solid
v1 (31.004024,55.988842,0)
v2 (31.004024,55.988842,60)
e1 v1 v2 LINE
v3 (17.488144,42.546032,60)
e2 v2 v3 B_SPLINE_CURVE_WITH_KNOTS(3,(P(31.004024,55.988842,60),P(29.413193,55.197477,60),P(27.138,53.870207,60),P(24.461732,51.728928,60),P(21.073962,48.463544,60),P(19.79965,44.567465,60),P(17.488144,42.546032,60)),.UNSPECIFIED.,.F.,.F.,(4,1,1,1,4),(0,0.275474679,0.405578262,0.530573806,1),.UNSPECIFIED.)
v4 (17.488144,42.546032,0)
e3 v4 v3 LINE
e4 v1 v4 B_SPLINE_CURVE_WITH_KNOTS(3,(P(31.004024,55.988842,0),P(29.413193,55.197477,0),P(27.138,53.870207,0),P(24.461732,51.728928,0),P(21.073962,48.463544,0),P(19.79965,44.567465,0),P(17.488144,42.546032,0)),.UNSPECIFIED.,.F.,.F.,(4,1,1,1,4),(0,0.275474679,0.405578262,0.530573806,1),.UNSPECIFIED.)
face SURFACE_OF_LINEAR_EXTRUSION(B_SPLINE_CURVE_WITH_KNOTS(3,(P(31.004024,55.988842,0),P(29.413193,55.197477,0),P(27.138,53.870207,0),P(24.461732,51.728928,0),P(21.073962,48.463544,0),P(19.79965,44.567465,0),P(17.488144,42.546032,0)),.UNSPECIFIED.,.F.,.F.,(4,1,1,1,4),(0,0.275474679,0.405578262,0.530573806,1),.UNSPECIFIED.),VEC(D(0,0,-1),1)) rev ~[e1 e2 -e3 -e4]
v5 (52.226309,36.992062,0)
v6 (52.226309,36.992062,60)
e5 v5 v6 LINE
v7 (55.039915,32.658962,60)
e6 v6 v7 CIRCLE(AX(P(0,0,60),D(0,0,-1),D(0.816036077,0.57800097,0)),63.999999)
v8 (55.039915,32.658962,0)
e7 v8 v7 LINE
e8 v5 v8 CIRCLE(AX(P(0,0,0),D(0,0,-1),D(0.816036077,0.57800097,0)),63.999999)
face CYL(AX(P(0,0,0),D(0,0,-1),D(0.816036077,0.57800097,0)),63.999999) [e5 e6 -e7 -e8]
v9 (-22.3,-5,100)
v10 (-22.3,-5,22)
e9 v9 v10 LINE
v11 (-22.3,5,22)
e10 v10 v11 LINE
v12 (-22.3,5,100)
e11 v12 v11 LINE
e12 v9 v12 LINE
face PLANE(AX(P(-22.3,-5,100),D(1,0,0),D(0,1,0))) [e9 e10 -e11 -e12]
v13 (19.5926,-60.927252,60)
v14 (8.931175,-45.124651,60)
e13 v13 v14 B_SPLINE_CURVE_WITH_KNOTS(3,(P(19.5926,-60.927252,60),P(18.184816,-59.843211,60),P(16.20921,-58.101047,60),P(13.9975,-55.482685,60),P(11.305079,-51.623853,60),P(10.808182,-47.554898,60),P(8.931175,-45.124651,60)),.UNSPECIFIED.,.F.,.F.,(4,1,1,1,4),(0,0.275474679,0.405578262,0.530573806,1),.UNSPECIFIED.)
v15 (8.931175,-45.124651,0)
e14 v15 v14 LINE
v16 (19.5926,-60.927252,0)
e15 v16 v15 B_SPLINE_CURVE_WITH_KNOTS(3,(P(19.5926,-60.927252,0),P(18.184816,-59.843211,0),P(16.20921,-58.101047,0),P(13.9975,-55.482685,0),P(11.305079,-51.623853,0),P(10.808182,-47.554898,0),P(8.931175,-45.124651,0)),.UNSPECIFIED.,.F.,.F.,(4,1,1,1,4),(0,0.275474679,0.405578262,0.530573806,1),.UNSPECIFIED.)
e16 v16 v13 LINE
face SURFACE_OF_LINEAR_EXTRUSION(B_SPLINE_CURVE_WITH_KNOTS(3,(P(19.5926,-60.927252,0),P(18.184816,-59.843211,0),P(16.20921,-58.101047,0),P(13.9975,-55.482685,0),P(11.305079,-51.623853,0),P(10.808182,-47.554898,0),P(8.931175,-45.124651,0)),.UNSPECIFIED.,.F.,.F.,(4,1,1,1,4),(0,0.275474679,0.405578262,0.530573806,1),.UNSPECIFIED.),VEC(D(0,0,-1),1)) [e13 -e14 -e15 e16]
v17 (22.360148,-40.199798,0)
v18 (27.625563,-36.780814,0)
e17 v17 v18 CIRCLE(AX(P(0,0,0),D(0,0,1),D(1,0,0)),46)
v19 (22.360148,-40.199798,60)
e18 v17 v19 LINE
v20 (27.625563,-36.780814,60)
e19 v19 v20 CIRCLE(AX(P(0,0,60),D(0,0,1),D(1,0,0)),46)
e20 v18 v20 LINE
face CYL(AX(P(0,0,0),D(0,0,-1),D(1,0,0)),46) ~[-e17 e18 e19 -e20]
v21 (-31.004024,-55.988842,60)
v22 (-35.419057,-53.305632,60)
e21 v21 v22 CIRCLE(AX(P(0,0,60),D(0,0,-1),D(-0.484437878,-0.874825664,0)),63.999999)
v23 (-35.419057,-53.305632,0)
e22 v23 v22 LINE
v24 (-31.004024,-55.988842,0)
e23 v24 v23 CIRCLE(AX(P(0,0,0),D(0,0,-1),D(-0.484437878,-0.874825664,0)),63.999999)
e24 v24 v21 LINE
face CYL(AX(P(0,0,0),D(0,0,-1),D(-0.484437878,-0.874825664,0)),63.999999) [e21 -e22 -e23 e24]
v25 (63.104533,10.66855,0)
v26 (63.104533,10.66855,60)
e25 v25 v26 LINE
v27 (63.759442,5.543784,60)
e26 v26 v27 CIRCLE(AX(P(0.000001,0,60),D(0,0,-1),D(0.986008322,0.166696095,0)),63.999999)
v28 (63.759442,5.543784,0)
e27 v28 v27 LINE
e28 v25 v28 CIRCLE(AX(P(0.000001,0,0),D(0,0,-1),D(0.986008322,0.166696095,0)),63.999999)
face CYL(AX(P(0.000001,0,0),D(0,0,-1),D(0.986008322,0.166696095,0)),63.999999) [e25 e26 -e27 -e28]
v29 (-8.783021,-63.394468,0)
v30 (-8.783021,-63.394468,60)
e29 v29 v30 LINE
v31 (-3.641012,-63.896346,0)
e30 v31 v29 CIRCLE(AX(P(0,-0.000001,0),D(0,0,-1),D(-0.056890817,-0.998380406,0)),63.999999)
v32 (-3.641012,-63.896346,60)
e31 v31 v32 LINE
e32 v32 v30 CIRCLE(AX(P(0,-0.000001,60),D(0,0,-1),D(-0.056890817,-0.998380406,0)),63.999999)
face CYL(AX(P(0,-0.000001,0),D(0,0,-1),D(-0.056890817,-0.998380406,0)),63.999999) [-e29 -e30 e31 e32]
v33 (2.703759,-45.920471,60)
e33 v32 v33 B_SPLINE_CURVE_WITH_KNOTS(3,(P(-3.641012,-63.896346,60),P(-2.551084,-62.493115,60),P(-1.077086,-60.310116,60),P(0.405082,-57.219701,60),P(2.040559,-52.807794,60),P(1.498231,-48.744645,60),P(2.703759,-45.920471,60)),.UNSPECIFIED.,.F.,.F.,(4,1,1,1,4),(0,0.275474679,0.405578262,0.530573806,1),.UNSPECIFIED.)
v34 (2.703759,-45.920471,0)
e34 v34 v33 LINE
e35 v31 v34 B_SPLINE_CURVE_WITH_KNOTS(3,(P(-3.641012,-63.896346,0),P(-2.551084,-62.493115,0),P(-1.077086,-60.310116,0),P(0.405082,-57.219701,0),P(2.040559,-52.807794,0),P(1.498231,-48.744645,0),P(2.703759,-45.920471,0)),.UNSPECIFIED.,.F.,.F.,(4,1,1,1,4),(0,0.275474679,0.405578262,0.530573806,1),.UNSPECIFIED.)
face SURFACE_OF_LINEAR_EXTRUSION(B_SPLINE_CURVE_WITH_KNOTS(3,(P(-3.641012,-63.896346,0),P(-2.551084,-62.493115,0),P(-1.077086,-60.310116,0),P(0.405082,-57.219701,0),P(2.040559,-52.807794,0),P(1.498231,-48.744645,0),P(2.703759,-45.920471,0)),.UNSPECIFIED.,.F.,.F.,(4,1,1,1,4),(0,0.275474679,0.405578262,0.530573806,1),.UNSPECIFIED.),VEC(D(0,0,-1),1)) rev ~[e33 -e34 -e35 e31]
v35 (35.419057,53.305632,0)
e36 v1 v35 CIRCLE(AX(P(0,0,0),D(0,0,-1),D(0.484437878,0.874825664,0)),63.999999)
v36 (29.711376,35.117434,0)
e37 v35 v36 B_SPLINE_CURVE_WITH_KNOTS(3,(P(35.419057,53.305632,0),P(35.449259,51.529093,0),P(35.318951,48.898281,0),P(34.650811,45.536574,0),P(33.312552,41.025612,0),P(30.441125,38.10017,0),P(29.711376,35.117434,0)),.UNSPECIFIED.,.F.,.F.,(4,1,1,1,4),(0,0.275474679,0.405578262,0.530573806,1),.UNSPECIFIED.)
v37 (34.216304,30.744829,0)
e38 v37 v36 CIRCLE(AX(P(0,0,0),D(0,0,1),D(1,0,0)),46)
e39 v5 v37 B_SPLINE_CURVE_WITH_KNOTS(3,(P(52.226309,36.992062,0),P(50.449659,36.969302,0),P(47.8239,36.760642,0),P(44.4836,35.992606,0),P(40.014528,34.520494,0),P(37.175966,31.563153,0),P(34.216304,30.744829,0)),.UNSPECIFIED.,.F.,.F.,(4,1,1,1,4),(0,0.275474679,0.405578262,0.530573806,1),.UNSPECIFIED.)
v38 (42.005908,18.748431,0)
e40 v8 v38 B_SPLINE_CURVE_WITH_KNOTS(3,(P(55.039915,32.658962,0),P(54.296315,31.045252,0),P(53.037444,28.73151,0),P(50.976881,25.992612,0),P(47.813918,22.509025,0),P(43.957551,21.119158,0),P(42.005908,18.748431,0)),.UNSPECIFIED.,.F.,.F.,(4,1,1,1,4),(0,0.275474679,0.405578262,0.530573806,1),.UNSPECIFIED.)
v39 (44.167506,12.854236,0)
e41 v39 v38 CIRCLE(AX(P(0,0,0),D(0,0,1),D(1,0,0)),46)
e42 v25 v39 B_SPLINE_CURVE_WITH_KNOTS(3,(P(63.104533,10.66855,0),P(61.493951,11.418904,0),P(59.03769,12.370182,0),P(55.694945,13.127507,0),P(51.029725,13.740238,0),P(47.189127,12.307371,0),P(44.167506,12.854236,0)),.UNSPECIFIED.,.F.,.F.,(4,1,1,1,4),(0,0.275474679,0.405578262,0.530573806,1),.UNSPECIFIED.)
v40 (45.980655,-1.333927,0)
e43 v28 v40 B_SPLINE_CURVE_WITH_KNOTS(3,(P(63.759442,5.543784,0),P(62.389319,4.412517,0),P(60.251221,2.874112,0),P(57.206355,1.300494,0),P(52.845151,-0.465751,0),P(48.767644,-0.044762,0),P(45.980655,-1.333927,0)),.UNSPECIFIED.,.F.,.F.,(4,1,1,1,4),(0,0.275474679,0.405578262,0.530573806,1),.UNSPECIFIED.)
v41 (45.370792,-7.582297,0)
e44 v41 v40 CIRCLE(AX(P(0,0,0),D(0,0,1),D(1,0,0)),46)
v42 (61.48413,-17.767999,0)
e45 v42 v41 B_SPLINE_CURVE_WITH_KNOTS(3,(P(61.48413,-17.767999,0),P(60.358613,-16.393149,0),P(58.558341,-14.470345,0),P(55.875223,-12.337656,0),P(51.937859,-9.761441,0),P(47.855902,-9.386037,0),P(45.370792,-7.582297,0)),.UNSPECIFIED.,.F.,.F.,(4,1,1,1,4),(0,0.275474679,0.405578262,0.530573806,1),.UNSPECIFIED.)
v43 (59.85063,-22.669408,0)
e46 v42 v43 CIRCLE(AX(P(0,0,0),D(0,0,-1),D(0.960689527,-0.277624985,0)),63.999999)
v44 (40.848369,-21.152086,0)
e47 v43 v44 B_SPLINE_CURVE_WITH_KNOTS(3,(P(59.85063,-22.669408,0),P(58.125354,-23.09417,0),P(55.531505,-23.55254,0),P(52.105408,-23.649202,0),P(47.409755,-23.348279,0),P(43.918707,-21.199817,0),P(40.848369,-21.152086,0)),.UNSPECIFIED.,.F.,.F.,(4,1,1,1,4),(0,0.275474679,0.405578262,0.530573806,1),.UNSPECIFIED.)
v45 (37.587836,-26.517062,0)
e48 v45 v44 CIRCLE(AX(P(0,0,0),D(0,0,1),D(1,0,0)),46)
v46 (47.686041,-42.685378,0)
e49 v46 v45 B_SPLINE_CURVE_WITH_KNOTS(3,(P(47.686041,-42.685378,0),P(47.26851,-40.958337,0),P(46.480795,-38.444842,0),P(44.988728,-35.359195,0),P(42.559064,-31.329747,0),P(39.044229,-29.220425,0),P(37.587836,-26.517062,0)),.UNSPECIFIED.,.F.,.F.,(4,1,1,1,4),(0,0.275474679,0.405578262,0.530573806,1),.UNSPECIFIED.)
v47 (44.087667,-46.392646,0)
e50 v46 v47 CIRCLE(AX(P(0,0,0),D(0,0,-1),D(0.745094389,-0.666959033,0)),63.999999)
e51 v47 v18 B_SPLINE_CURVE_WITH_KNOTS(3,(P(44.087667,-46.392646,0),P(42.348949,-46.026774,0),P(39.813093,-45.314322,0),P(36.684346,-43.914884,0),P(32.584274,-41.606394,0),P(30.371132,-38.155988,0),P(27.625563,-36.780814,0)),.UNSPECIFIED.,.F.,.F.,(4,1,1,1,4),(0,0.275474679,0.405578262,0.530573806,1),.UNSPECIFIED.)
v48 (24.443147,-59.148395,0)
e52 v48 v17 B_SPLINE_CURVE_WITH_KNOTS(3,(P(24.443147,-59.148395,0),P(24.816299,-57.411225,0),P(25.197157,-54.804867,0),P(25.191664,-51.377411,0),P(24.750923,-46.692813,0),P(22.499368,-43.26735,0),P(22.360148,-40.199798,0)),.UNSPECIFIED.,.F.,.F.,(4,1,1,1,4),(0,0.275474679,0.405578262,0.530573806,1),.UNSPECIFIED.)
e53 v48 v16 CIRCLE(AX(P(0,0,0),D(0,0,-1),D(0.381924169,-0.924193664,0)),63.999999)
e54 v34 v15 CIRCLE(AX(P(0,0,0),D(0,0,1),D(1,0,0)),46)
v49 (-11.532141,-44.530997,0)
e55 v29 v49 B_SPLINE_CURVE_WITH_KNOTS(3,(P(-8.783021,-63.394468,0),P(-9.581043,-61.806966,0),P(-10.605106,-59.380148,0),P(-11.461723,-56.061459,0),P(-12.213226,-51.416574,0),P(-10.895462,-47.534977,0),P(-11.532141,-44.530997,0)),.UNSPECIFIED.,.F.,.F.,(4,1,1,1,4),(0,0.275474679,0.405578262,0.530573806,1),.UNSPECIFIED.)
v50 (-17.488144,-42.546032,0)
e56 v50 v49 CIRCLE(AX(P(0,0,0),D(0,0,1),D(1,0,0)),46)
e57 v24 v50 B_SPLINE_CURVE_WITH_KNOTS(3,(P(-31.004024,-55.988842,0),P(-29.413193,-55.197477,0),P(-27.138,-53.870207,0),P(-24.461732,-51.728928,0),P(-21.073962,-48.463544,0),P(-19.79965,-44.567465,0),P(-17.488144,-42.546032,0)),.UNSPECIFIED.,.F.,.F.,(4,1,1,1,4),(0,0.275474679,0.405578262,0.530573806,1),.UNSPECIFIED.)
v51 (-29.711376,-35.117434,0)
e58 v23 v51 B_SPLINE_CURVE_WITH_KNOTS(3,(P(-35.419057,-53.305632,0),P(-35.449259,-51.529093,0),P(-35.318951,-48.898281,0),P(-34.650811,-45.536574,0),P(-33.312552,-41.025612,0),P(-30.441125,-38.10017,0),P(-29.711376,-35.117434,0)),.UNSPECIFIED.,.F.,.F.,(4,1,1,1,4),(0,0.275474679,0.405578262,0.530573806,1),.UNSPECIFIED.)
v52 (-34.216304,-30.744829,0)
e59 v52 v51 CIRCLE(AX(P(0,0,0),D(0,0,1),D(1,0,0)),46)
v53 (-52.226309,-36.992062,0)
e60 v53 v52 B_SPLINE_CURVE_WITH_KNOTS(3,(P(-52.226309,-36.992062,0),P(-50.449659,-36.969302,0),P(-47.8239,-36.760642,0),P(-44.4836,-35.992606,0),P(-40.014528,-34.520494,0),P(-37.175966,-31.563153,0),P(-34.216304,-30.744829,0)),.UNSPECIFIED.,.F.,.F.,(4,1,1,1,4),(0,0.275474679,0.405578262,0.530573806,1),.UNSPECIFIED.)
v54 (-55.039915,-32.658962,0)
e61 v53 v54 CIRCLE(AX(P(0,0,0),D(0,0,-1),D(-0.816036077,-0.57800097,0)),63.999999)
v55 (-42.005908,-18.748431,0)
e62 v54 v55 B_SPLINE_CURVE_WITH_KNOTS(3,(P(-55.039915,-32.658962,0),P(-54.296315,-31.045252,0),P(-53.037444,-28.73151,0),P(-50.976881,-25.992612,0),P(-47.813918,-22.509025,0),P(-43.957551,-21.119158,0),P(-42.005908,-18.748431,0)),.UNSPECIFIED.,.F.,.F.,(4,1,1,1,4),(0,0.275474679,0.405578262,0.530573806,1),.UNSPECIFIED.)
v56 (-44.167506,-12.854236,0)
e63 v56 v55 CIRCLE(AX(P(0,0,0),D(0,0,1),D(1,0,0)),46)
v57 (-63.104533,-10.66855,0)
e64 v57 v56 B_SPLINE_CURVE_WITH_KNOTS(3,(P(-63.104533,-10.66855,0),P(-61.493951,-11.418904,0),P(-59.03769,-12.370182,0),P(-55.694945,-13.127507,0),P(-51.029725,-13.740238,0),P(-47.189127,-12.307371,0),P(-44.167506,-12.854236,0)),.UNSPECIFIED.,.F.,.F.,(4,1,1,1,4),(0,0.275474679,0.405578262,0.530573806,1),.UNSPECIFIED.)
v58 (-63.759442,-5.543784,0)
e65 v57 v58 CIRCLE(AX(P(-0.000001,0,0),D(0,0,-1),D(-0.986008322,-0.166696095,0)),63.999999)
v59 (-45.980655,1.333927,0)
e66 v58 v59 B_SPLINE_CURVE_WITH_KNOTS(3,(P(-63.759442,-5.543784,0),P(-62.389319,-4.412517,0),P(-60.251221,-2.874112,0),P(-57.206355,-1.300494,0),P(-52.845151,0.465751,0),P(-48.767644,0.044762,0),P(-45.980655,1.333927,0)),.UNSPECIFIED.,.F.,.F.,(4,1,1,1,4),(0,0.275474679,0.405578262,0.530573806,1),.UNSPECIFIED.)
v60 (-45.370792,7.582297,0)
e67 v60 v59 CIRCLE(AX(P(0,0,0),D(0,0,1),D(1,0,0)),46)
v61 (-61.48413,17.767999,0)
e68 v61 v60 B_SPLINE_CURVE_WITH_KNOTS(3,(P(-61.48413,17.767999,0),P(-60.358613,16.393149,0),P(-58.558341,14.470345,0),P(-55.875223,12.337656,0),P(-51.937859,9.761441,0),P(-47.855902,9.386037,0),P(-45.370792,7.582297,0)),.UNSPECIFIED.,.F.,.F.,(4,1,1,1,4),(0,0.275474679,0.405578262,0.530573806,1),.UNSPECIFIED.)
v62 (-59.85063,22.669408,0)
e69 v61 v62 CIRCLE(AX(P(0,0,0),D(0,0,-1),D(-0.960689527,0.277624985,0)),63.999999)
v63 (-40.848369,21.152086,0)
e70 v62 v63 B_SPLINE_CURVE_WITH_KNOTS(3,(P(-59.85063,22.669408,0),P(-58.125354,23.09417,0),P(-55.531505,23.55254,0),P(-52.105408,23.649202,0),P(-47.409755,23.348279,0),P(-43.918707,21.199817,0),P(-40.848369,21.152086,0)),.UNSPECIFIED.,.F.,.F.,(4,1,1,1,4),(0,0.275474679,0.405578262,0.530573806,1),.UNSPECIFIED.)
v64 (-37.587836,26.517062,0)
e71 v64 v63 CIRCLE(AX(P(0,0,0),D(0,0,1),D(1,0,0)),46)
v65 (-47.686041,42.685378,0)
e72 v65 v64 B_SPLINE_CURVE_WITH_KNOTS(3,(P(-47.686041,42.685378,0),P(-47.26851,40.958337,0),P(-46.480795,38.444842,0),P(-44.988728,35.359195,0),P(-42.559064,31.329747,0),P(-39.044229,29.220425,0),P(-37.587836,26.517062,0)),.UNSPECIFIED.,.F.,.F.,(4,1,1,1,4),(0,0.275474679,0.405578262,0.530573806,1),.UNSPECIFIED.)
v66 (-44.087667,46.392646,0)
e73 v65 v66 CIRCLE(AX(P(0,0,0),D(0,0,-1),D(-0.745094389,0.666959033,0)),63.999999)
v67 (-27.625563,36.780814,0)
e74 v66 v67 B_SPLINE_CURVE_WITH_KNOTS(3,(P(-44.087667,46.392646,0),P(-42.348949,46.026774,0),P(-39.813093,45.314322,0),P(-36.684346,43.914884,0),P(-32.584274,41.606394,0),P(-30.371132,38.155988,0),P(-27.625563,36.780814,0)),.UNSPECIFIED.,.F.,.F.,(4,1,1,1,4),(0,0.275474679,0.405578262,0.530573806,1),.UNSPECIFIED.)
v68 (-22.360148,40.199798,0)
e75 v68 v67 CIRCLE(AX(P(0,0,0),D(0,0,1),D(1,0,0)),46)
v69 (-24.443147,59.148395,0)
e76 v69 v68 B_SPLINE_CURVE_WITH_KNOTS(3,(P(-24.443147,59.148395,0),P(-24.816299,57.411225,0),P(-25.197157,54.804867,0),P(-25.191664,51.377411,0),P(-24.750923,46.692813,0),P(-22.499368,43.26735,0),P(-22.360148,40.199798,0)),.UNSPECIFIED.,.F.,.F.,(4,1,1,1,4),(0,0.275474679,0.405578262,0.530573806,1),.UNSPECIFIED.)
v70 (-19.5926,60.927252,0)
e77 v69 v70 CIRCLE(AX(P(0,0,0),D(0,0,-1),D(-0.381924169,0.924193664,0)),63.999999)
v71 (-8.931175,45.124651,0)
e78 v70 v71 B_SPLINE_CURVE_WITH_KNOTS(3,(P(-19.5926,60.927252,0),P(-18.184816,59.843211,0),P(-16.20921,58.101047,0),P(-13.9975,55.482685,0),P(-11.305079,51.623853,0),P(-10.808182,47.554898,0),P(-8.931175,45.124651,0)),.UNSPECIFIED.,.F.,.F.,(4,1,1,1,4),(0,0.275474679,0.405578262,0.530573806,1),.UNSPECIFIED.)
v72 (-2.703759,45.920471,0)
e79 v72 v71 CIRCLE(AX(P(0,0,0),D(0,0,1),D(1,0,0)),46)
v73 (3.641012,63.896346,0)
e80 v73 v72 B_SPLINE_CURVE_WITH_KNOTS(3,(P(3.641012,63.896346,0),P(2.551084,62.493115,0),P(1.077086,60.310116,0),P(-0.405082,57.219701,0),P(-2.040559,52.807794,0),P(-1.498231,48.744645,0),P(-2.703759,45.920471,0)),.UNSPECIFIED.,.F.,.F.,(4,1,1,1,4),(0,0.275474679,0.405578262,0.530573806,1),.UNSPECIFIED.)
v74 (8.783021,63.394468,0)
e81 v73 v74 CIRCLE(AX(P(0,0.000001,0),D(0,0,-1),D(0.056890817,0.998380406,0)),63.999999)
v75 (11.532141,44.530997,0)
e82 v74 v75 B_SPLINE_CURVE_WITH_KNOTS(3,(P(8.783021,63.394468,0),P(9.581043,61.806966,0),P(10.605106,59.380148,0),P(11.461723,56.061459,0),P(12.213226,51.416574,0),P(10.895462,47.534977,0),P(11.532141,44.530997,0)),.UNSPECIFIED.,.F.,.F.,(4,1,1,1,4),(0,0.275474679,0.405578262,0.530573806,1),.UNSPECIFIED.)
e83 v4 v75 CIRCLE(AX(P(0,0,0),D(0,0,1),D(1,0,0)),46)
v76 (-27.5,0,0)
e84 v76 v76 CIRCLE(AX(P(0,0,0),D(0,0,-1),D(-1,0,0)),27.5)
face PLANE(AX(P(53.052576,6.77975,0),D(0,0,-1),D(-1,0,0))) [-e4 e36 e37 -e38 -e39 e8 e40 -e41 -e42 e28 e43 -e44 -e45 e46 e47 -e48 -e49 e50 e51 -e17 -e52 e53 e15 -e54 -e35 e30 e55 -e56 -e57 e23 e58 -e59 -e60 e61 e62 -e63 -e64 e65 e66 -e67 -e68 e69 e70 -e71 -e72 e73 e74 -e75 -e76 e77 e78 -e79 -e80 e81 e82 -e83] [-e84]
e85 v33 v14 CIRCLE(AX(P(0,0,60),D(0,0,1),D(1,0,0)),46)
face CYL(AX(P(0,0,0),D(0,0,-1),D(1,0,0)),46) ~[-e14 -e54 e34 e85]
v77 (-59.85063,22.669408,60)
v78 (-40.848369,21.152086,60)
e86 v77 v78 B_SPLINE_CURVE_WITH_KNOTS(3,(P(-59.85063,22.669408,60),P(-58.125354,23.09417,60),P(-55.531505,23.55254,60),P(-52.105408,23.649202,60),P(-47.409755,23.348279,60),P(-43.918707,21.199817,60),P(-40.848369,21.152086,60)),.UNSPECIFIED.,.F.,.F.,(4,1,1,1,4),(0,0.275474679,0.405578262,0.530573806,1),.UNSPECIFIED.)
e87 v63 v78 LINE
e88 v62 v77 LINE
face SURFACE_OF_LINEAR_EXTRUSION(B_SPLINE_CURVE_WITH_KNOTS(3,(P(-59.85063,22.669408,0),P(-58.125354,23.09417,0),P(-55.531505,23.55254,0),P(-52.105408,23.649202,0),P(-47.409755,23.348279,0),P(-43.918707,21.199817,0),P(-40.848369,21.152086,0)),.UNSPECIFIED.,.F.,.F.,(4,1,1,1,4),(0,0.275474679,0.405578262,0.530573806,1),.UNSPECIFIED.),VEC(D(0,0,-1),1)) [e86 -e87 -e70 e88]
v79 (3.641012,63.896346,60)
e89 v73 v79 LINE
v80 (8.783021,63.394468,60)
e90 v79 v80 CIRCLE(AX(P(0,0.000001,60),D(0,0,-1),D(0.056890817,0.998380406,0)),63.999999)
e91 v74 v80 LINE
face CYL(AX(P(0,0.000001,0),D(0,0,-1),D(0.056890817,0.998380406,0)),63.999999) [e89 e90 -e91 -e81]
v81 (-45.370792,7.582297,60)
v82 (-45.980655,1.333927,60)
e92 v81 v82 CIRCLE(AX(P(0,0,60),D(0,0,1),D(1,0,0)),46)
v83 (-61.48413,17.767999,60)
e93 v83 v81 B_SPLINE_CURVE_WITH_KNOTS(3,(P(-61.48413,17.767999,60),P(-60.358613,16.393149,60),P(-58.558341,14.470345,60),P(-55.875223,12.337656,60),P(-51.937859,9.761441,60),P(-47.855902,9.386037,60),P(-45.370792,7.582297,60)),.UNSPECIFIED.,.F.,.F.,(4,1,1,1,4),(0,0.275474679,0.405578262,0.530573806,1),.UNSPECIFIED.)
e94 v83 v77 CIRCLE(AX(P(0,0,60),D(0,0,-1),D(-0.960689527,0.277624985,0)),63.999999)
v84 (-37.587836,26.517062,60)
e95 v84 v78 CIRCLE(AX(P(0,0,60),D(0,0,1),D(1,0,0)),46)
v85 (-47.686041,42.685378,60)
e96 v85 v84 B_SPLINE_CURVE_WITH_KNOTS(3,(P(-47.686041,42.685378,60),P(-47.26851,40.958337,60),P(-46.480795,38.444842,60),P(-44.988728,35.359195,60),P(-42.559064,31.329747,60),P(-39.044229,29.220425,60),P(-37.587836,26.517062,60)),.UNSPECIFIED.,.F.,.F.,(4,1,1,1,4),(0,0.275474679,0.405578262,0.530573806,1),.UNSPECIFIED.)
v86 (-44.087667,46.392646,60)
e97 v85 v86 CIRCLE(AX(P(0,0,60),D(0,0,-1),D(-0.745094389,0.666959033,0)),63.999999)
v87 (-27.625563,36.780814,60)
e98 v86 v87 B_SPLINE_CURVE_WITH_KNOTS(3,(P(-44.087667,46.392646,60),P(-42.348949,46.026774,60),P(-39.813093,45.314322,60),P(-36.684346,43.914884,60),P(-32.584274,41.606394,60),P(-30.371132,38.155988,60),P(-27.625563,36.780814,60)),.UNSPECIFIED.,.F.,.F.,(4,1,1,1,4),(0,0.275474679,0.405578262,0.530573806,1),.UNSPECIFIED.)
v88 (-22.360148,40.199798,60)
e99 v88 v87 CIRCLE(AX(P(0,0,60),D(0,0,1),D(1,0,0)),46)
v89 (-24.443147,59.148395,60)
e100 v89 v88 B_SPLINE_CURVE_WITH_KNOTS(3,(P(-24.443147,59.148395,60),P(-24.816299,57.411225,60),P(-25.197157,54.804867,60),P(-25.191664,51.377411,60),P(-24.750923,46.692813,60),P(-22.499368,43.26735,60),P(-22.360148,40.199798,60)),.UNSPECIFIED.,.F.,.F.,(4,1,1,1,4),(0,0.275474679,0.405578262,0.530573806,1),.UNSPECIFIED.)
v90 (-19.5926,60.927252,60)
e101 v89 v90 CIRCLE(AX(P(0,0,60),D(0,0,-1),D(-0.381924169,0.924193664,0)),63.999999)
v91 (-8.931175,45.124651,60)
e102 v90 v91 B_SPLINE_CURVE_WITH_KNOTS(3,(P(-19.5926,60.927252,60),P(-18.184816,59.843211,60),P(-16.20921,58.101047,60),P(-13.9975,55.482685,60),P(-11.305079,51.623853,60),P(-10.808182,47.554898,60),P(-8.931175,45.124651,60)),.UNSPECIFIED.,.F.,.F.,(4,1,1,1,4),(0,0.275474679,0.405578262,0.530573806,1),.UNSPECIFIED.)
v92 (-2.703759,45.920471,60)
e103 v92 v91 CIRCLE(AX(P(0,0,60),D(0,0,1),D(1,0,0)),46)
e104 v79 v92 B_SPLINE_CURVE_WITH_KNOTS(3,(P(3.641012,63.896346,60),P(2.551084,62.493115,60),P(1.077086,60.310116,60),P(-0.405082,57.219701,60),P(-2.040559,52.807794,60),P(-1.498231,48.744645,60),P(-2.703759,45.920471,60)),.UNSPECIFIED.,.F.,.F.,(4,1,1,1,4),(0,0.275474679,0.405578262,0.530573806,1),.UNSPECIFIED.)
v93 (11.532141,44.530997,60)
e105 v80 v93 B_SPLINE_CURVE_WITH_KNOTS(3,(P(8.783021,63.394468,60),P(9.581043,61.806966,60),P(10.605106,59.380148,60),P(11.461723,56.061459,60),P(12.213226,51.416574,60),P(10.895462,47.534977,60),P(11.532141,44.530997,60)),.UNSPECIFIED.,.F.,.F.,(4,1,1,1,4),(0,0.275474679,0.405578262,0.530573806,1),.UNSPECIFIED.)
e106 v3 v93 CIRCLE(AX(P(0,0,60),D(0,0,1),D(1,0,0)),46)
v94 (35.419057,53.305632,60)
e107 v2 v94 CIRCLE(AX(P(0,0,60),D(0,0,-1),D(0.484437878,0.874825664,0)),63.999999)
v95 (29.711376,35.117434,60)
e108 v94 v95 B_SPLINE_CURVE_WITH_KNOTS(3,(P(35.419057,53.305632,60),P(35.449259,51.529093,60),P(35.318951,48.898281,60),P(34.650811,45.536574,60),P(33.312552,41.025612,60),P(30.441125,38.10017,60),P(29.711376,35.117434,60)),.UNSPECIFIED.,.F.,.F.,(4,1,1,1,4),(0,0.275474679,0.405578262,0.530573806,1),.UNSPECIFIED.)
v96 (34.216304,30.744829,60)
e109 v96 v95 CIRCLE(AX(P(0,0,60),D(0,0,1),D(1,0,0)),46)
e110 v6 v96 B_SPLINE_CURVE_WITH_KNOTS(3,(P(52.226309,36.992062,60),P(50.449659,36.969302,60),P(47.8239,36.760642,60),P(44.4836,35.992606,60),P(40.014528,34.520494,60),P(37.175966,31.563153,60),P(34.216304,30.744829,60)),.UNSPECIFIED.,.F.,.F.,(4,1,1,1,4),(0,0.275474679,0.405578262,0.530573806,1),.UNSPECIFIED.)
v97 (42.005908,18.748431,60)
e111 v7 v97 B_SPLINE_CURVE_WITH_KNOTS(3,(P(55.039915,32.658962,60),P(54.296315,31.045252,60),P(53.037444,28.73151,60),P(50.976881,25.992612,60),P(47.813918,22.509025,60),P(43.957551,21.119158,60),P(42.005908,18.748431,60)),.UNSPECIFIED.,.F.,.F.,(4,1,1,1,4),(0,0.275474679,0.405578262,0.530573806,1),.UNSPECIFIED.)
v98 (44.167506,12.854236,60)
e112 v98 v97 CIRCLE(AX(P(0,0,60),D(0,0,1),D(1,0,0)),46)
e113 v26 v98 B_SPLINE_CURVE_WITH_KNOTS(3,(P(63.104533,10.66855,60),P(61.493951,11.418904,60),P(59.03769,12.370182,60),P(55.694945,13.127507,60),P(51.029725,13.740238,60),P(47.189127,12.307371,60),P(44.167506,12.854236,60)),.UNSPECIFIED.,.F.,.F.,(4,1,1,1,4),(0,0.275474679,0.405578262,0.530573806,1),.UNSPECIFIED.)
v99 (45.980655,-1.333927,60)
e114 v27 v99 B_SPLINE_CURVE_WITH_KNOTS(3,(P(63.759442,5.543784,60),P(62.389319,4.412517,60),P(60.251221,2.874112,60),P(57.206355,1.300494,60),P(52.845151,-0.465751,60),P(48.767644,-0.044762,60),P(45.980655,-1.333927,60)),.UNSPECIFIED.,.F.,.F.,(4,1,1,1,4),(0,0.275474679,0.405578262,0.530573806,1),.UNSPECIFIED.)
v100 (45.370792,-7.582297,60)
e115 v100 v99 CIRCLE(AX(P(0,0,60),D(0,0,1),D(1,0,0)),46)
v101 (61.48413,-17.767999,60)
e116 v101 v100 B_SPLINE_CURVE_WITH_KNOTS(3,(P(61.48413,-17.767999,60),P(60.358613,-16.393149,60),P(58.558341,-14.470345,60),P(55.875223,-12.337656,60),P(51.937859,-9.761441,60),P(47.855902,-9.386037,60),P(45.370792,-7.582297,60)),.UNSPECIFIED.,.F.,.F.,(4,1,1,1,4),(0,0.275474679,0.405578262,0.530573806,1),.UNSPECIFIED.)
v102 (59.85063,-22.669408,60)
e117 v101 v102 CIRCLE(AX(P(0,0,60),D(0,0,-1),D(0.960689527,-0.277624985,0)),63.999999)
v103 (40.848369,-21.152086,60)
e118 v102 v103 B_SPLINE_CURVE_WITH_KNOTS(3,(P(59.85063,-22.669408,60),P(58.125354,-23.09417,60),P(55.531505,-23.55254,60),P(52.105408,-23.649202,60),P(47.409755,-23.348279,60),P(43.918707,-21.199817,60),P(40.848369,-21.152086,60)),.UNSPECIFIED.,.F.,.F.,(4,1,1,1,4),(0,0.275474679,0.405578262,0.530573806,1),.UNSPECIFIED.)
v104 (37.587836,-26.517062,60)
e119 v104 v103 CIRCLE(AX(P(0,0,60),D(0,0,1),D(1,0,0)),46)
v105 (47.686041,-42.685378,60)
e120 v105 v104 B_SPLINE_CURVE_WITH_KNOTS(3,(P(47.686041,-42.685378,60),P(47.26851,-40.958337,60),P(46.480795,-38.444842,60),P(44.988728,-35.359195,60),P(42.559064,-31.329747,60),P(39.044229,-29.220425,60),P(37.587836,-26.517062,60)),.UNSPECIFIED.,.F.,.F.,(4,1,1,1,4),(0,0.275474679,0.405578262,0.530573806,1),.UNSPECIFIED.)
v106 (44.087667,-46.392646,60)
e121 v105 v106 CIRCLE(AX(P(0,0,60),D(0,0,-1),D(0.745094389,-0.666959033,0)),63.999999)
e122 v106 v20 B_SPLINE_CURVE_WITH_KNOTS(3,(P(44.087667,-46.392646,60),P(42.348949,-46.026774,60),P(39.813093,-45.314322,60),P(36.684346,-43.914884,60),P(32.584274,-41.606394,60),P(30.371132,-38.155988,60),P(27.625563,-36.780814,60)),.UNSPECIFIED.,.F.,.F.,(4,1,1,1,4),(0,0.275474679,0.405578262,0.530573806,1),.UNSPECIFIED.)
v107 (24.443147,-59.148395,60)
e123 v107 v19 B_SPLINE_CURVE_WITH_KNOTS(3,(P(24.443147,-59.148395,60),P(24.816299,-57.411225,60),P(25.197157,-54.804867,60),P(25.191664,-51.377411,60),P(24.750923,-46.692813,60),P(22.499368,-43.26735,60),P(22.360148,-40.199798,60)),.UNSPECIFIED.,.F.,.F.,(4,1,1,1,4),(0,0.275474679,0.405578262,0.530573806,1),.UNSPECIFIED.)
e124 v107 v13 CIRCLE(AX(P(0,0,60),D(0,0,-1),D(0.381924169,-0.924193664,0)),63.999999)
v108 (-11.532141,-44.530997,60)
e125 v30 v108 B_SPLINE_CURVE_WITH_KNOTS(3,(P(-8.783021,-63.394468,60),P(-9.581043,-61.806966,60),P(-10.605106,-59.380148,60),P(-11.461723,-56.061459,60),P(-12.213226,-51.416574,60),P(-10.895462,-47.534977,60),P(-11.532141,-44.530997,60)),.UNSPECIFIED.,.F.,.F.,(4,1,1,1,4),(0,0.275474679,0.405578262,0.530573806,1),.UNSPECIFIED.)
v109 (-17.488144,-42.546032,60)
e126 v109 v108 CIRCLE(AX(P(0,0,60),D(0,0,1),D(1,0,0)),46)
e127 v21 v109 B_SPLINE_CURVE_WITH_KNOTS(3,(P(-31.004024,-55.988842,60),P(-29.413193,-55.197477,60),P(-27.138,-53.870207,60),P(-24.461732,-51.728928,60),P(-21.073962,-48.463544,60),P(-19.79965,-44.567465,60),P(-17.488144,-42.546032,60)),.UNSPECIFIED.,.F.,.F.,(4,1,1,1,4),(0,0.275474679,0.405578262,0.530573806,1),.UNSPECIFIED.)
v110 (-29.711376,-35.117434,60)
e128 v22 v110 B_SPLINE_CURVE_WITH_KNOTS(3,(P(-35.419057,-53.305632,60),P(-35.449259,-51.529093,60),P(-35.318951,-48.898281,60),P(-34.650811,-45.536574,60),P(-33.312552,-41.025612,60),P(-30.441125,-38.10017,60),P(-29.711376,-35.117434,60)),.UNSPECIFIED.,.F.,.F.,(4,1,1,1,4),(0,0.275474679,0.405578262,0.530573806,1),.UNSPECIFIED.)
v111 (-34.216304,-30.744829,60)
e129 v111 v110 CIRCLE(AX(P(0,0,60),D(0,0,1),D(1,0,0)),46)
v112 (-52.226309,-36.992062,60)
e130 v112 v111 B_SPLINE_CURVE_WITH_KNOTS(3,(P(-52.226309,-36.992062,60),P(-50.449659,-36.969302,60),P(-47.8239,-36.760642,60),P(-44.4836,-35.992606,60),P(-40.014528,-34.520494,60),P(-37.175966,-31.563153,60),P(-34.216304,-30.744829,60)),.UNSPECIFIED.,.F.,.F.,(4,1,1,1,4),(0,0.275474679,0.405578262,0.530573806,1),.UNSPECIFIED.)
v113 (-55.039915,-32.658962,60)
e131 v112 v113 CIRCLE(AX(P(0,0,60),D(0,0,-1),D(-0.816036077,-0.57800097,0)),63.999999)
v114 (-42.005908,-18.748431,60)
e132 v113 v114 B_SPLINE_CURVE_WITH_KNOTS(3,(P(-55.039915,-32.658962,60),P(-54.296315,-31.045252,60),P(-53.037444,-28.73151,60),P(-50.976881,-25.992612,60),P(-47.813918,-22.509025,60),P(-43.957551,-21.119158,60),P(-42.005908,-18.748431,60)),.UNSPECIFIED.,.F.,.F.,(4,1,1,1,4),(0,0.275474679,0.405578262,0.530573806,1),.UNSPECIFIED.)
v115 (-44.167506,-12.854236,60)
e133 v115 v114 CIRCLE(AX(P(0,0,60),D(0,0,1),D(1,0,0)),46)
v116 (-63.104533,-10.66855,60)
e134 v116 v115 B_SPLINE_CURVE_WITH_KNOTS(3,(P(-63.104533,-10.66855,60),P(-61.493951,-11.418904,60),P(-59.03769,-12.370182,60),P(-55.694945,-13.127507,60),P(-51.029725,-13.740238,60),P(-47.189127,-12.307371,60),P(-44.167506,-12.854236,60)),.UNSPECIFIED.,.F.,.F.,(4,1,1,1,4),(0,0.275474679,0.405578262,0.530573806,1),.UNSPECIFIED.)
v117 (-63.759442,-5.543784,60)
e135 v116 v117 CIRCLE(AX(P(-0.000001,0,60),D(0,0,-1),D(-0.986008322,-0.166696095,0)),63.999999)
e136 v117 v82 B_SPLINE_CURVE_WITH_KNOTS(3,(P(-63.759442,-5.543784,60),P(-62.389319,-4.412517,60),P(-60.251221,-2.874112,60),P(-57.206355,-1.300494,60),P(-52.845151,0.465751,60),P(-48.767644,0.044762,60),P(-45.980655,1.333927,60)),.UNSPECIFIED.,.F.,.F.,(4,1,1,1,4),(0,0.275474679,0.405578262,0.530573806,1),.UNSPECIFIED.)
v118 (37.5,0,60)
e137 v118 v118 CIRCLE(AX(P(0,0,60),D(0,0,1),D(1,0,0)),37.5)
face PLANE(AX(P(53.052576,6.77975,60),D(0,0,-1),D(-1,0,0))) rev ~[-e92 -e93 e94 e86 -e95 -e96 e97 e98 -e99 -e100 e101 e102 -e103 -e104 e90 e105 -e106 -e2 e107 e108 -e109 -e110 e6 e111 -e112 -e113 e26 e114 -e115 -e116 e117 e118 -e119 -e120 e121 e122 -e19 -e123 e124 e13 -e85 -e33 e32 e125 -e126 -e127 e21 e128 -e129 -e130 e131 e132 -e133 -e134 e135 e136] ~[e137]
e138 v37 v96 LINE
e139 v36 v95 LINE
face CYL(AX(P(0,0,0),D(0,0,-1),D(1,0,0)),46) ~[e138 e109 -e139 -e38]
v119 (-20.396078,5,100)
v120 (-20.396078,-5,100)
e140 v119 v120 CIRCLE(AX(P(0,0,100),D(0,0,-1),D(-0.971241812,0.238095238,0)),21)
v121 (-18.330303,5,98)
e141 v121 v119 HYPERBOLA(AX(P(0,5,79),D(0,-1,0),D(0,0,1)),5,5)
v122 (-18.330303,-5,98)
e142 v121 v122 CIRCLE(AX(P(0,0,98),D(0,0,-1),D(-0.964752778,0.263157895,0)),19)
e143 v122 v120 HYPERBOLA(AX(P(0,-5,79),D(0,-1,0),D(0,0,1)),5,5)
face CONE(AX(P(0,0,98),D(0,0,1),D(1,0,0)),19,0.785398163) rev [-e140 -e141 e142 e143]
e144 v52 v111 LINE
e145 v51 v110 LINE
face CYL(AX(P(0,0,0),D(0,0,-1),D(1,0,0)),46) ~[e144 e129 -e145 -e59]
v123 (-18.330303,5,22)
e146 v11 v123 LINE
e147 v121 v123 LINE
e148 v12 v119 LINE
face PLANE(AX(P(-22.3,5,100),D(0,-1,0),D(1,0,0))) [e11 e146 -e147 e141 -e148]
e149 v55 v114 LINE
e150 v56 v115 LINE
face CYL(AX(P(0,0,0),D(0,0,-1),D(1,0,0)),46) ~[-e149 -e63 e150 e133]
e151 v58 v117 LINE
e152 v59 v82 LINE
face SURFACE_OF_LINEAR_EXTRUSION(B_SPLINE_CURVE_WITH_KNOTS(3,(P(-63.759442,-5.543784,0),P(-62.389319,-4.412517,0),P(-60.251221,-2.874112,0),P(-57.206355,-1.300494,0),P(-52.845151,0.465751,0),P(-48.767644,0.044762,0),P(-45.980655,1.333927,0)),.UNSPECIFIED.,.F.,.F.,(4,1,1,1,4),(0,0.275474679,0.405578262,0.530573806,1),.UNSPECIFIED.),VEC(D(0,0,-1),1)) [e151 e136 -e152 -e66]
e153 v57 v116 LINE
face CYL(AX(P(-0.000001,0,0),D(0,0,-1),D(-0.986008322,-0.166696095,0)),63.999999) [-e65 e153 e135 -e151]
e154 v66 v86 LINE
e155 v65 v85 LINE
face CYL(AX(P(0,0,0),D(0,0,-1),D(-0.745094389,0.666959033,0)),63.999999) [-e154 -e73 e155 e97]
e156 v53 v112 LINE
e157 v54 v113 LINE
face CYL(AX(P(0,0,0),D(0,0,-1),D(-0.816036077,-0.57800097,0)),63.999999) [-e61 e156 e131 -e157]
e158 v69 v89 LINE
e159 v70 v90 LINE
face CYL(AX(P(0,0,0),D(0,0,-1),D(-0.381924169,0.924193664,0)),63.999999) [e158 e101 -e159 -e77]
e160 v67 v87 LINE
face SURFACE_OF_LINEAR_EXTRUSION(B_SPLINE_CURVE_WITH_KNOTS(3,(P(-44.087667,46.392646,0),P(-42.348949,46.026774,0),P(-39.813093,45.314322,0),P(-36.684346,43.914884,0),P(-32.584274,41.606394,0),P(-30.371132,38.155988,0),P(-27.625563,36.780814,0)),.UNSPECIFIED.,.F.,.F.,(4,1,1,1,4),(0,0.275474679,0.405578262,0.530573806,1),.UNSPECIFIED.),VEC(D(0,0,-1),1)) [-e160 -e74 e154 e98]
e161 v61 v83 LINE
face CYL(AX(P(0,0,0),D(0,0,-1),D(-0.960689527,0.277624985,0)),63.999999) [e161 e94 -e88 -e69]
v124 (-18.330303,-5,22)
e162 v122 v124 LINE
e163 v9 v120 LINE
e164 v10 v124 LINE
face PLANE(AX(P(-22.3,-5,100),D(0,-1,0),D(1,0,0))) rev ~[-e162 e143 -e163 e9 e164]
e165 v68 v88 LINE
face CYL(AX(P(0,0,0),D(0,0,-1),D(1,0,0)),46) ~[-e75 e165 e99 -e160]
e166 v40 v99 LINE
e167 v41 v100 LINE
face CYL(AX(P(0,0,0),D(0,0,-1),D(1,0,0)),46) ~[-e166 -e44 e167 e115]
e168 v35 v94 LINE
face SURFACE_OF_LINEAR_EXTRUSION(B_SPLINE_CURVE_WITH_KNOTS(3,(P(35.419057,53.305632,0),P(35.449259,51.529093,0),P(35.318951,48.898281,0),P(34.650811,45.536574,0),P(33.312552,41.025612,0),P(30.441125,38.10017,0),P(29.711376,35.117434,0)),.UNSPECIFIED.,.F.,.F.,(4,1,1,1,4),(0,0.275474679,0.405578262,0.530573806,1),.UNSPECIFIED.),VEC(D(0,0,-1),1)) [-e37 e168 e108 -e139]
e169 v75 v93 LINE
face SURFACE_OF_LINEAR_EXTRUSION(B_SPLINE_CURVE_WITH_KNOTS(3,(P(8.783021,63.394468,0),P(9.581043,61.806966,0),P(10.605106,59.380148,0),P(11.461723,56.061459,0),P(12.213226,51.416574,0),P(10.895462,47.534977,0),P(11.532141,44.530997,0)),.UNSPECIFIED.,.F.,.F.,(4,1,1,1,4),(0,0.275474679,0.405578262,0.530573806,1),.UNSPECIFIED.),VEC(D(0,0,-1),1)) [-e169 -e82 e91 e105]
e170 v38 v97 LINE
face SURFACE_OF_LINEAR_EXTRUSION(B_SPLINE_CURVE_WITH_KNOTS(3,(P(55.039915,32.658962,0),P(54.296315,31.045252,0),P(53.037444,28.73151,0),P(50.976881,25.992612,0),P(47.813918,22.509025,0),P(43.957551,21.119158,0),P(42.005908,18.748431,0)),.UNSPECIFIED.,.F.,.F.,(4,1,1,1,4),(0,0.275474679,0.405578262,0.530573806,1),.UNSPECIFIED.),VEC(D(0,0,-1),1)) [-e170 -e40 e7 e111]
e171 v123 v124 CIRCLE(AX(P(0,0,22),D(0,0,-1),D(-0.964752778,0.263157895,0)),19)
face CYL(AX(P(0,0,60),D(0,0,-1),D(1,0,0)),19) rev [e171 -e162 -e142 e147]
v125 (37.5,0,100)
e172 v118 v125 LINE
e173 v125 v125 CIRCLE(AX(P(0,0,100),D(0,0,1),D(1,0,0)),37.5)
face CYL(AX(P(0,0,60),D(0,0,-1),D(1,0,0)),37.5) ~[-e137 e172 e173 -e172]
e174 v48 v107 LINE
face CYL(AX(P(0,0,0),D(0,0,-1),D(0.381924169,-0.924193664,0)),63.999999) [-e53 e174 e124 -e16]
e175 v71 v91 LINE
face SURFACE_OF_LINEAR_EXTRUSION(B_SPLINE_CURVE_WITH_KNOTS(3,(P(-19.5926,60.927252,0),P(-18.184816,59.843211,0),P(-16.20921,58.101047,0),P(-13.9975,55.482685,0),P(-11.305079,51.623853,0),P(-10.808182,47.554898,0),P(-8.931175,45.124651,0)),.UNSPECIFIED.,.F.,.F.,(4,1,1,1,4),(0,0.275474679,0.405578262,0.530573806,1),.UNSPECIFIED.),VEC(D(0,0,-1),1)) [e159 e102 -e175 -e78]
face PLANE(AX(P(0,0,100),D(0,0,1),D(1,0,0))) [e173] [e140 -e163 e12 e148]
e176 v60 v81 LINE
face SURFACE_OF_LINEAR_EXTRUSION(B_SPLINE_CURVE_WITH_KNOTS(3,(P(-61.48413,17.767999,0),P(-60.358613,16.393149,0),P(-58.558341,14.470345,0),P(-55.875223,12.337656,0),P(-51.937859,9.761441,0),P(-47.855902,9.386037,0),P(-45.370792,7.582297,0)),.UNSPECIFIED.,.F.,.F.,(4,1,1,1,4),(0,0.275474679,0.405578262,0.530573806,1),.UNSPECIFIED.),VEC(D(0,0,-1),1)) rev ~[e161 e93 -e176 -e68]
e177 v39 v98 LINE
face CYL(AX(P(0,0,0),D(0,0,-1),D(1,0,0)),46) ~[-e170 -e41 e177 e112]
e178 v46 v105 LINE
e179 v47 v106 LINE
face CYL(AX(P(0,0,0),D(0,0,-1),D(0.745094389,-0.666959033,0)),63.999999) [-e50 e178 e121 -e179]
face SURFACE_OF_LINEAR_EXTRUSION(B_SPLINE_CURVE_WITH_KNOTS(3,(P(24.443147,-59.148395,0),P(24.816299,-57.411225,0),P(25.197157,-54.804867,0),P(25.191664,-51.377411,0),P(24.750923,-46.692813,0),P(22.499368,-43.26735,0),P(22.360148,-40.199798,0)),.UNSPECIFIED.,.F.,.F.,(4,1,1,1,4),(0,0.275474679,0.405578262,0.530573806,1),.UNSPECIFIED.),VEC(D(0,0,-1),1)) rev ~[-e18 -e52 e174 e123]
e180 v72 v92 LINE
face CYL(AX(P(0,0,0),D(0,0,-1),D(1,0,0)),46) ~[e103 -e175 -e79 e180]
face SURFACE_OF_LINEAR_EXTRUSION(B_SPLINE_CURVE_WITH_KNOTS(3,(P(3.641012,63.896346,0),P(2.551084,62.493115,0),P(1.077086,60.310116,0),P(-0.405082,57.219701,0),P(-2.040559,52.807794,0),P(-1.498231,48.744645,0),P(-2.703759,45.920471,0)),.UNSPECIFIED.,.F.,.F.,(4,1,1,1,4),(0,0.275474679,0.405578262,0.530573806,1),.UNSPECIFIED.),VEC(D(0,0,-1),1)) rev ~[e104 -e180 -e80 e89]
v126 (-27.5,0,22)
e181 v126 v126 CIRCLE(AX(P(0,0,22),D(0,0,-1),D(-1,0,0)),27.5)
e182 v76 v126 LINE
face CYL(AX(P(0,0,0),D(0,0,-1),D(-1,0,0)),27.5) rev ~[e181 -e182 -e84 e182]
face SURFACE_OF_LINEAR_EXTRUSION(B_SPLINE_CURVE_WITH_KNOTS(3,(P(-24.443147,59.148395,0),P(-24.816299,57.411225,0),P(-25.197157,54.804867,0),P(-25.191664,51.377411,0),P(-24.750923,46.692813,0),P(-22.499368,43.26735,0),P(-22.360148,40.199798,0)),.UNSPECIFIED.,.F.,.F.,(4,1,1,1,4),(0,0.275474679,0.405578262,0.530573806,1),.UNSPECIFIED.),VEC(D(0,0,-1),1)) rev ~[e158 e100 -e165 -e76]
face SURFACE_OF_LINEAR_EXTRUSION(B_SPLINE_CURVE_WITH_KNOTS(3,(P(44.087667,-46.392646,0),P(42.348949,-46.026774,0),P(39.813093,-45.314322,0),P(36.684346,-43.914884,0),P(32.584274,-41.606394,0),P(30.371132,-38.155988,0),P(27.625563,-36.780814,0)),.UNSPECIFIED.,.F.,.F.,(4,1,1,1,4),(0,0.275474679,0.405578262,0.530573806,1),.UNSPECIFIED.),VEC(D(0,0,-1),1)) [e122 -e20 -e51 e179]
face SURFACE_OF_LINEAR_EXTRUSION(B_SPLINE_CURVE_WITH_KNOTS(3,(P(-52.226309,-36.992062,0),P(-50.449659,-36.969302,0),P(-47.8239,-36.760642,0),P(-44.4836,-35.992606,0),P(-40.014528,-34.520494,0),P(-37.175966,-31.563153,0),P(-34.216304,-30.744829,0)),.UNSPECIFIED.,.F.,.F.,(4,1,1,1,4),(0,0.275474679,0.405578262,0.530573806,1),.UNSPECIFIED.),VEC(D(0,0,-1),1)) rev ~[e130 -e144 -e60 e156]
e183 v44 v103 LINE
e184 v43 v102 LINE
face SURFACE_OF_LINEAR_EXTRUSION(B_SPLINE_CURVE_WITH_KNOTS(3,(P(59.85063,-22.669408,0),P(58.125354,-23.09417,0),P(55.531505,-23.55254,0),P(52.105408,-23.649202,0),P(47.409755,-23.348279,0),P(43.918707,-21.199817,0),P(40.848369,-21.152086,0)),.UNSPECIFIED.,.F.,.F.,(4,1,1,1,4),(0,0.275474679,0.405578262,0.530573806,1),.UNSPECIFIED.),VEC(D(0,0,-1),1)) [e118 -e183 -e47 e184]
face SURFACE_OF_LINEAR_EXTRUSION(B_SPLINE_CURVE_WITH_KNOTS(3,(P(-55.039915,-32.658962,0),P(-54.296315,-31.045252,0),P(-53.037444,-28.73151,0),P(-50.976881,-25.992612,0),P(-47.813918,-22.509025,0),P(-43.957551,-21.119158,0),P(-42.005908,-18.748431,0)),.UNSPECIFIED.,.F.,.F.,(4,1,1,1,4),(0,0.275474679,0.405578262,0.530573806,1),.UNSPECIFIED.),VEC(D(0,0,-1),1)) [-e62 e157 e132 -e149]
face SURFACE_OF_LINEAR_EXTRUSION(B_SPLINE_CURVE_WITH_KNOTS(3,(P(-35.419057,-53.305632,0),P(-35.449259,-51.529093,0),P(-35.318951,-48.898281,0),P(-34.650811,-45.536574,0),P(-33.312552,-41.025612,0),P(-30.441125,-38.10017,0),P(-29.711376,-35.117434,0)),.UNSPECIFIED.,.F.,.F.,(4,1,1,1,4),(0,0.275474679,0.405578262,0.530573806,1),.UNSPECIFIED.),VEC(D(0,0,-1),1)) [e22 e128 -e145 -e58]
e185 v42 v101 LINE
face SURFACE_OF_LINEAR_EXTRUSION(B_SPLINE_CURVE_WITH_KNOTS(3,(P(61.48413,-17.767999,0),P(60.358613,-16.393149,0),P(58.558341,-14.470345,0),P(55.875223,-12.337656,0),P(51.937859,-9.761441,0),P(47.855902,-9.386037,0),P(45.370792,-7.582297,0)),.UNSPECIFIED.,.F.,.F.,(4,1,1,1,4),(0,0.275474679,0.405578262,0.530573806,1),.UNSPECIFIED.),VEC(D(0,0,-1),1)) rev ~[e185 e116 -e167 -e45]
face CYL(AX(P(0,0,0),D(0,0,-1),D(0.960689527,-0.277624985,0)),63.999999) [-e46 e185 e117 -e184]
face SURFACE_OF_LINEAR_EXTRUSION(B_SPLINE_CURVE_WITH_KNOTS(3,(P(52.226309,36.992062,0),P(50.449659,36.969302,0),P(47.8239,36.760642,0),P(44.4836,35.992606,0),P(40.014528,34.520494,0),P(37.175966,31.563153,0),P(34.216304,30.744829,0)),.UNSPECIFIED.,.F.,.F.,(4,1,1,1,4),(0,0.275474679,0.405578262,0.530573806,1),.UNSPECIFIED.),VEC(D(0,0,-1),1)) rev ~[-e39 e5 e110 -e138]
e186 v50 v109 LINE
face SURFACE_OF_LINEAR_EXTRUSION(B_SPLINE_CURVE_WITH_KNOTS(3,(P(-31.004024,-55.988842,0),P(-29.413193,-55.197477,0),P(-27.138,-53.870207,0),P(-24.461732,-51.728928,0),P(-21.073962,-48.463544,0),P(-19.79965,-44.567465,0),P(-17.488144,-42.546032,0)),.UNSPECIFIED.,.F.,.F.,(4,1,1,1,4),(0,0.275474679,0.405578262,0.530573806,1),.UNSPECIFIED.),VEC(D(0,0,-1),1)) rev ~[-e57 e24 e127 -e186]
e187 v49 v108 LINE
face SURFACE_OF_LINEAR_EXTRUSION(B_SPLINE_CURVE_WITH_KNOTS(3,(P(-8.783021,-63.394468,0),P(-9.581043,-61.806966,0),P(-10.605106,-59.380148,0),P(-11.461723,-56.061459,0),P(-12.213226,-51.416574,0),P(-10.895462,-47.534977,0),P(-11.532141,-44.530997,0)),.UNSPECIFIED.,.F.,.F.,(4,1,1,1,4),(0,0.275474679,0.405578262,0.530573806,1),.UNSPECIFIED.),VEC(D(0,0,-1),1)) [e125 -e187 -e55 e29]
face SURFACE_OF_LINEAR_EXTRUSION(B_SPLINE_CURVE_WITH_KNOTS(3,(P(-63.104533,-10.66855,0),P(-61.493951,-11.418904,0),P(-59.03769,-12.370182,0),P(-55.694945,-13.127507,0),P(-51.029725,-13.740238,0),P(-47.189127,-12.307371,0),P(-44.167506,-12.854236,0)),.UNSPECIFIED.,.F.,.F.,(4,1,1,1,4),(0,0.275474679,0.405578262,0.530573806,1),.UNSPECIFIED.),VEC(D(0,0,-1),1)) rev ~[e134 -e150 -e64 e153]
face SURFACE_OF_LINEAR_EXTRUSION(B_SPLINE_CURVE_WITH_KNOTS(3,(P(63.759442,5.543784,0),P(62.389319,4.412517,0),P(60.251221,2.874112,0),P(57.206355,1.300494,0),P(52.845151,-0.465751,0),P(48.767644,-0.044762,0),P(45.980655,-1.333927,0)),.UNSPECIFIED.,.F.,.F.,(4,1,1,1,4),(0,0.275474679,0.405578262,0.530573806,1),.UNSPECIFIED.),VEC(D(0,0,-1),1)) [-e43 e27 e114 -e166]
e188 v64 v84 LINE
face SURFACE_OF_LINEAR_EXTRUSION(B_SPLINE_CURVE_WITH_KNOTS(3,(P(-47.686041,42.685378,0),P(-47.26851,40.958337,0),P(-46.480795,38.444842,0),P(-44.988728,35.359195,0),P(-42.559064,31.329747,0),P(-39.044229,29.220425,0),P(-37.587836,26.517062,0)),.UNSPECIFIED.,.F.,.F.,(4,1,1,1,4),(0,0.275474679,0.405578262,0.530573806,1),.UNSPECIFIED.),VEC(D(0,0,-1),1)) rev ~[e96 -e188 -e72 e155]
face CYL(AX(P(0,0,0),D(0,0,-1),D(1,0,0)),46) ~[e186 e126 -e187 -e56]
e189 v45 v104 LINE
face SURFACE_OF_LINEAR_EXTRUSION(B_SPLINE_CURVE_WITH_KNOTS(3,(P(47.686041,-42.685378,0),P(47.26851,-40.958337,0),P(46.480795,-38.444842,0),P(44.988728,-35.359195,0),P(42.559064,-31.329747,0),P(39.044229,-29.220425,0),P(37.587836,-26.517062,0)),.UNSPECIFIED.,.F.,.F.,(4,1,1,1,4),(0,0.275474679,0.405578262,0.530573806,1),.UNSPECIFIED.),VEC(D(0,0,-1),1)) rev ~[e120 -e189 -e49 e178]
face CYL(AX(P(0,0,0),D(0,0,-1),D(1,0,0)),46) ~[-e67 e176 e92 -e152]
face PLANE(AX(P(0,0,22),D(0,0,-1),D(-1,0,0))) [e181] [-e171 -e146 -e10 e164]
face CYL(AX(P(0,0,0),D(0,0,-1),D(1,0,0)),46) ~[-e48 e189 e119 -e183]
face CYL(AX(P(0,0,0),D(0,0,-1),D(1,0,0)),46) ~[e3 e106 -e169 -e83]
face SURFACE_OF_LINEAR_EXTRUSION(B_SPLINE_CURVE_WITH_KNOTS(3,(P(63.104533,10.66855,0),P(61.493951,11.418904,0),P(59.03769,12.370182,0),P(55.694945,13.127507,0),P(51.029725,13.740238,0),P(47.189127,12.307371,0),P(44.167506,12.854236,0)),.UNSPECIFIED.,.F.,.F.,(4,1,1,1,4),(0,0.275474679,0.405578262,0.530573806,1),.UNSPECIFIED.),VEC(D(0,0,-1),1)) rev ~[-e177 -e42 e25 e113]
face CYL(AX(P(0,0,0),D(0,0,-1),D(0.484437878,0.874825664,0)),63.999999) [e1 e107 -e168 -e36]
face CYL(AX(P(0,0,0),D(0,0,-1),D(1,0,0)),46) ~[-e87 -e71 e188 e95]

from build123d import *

# Parameters (mm, degrees)
SKETCH1_R           = 46
SKETCH1_R_2         = 19
BOSS_EXTRUDE1_DEPTH = 60
BOSS_EXTRUDE2_DEPTH = 60
CIRPATTERN1_COUNT   = 14
SKETCH3_R           = 37.5
SKETCH3_R_2         = 19
BOSS_EXTRUDE3_DEPTH = 40
SKETCH4_R           = 27.5
CUT_EXTRUDE1_DEPTH  = 22
CHAMFER1_SIZE       = 2
CUT_EXTRUDE2_REACH  = 136.715
SKETCH5_W           = 6.6
SKETCH5_H           = 10


with BuildPart() as part:
    # Sketch1 → Boss-Extrude1 (new body)
    with BuildSketch(Plane.XY):
        Circle(SKETCH1_R)
        Circle(SKETCH1_R_2, mode=Mode.SUBTRACT)
    extrude(amount=BOSS_EXTRUDE1_DEPTH)

    # Sketch2 → Boss-Extrude2 (add)
    with BuildSketch(Plane.XY):
        with BuildLine():
            ThreePointArc((63.104532635, 10.668550086), (63.483720976, 8.112778259), (63.759442112, 5.543784043))
            add(Edge.make_bspline(
                [(63.759442112, 5.543784043), (62.389318996, 4.412517104), (60.251221393, 2.874111803), (57.206354902, 1.300494321), (52.845151495, -0.465750744), (48.767643844, -0.044762334), (45.980655038, -1.333927402)],
                knots=[0, 0, 0, 0, 0.275474679, 0.405578262, 0.530573806, 1, 1, 1, 1], degree=3))
            ThreePointArc((45.980655038, -1.333927402), (45.628924451, 5.831059374), (44.167506403, 12.854235805))
            add(Edge.make_bspline(
                [(63.104532635, 10.668550086), (61.493951486, 11.418903738), (59.037689651, 12.370181839), (55.694944892, 13.127507004), (51.029724893, 13.740237902), (47.189127109, 12.307370657), (44.167506403, 12.854235805)],
                knots=[0, 0, 0, 0, 0.275474679, 0.405578262, 0.530573806, 1, 1, 1, 1], degree=3))
        make_face()
    boss_extrude2 = extrude(amount=BOSS_EXTRUDE2_DEPTH)

    # CirPattern1: Boss-Extrude2 ×14 about axis
    cirpattern1_axis = Axis((0, 0, 60), (0, 0, -1))
    for i in range(1, CIRPATTERN1_COUNT):
        add(boss_extrude2.rotate(cirpattern1_axis, i * 360 / CIRPATTERN1_COUNT))

    # Sketch3 → Boss-Extrude3 (add)
    with BuildSketch(Plane.XY.offset(60)):
        Circle(SKETCH3_R)
        Circle(SKETCH3_R_2, mode=Mode.SUBTRACT)
    extrude(amount=BOSS_EXTRUDE3_DEPTH)

    # Sketch4 → Cut-Extrude1 (cut)
    with BuildSketch(Plane(origin=(0, 0, 0), x_dir=(-1, 0, 0), z_dir=(0, 0, -1))):
        Circle(SKETCH4_R)
    extrude(amount=-CUT_EXTRUDE1_DEPTH, mode=Mode.SUBTRACT)

    # Chamfer1
    chamfer1_edges = [part.edges().sort_by_distance(p)[0] for p in [
        (-19, 0, 100),
    ]]
    chamfer(chamfer1_edges, length=CHAMFER1_SIZE)

    # Sketch5 → Cut-Extrude2 (cut, up to next)
    with BuildSketch(Plane.XY.offset(100), mode=Mode.PRIVATE) as cut_extrude2_sk1:
        with Locations((-19, 0)):
            Rectangle(SKETCH5_W, SKETCH5_H)
    cut_extrude2_tool1 = extrude(cut_extrude2_sk1.sketch, amount=-CUT_EXTRUDE2_REACH, mode=Mode.PRIVATE) & part.part
    add(cut_extrude2_tool1.solids().sort_by_distance((-19, 0, 100))[0], mode=Mode.SUBTRACT)


solid = part.part
